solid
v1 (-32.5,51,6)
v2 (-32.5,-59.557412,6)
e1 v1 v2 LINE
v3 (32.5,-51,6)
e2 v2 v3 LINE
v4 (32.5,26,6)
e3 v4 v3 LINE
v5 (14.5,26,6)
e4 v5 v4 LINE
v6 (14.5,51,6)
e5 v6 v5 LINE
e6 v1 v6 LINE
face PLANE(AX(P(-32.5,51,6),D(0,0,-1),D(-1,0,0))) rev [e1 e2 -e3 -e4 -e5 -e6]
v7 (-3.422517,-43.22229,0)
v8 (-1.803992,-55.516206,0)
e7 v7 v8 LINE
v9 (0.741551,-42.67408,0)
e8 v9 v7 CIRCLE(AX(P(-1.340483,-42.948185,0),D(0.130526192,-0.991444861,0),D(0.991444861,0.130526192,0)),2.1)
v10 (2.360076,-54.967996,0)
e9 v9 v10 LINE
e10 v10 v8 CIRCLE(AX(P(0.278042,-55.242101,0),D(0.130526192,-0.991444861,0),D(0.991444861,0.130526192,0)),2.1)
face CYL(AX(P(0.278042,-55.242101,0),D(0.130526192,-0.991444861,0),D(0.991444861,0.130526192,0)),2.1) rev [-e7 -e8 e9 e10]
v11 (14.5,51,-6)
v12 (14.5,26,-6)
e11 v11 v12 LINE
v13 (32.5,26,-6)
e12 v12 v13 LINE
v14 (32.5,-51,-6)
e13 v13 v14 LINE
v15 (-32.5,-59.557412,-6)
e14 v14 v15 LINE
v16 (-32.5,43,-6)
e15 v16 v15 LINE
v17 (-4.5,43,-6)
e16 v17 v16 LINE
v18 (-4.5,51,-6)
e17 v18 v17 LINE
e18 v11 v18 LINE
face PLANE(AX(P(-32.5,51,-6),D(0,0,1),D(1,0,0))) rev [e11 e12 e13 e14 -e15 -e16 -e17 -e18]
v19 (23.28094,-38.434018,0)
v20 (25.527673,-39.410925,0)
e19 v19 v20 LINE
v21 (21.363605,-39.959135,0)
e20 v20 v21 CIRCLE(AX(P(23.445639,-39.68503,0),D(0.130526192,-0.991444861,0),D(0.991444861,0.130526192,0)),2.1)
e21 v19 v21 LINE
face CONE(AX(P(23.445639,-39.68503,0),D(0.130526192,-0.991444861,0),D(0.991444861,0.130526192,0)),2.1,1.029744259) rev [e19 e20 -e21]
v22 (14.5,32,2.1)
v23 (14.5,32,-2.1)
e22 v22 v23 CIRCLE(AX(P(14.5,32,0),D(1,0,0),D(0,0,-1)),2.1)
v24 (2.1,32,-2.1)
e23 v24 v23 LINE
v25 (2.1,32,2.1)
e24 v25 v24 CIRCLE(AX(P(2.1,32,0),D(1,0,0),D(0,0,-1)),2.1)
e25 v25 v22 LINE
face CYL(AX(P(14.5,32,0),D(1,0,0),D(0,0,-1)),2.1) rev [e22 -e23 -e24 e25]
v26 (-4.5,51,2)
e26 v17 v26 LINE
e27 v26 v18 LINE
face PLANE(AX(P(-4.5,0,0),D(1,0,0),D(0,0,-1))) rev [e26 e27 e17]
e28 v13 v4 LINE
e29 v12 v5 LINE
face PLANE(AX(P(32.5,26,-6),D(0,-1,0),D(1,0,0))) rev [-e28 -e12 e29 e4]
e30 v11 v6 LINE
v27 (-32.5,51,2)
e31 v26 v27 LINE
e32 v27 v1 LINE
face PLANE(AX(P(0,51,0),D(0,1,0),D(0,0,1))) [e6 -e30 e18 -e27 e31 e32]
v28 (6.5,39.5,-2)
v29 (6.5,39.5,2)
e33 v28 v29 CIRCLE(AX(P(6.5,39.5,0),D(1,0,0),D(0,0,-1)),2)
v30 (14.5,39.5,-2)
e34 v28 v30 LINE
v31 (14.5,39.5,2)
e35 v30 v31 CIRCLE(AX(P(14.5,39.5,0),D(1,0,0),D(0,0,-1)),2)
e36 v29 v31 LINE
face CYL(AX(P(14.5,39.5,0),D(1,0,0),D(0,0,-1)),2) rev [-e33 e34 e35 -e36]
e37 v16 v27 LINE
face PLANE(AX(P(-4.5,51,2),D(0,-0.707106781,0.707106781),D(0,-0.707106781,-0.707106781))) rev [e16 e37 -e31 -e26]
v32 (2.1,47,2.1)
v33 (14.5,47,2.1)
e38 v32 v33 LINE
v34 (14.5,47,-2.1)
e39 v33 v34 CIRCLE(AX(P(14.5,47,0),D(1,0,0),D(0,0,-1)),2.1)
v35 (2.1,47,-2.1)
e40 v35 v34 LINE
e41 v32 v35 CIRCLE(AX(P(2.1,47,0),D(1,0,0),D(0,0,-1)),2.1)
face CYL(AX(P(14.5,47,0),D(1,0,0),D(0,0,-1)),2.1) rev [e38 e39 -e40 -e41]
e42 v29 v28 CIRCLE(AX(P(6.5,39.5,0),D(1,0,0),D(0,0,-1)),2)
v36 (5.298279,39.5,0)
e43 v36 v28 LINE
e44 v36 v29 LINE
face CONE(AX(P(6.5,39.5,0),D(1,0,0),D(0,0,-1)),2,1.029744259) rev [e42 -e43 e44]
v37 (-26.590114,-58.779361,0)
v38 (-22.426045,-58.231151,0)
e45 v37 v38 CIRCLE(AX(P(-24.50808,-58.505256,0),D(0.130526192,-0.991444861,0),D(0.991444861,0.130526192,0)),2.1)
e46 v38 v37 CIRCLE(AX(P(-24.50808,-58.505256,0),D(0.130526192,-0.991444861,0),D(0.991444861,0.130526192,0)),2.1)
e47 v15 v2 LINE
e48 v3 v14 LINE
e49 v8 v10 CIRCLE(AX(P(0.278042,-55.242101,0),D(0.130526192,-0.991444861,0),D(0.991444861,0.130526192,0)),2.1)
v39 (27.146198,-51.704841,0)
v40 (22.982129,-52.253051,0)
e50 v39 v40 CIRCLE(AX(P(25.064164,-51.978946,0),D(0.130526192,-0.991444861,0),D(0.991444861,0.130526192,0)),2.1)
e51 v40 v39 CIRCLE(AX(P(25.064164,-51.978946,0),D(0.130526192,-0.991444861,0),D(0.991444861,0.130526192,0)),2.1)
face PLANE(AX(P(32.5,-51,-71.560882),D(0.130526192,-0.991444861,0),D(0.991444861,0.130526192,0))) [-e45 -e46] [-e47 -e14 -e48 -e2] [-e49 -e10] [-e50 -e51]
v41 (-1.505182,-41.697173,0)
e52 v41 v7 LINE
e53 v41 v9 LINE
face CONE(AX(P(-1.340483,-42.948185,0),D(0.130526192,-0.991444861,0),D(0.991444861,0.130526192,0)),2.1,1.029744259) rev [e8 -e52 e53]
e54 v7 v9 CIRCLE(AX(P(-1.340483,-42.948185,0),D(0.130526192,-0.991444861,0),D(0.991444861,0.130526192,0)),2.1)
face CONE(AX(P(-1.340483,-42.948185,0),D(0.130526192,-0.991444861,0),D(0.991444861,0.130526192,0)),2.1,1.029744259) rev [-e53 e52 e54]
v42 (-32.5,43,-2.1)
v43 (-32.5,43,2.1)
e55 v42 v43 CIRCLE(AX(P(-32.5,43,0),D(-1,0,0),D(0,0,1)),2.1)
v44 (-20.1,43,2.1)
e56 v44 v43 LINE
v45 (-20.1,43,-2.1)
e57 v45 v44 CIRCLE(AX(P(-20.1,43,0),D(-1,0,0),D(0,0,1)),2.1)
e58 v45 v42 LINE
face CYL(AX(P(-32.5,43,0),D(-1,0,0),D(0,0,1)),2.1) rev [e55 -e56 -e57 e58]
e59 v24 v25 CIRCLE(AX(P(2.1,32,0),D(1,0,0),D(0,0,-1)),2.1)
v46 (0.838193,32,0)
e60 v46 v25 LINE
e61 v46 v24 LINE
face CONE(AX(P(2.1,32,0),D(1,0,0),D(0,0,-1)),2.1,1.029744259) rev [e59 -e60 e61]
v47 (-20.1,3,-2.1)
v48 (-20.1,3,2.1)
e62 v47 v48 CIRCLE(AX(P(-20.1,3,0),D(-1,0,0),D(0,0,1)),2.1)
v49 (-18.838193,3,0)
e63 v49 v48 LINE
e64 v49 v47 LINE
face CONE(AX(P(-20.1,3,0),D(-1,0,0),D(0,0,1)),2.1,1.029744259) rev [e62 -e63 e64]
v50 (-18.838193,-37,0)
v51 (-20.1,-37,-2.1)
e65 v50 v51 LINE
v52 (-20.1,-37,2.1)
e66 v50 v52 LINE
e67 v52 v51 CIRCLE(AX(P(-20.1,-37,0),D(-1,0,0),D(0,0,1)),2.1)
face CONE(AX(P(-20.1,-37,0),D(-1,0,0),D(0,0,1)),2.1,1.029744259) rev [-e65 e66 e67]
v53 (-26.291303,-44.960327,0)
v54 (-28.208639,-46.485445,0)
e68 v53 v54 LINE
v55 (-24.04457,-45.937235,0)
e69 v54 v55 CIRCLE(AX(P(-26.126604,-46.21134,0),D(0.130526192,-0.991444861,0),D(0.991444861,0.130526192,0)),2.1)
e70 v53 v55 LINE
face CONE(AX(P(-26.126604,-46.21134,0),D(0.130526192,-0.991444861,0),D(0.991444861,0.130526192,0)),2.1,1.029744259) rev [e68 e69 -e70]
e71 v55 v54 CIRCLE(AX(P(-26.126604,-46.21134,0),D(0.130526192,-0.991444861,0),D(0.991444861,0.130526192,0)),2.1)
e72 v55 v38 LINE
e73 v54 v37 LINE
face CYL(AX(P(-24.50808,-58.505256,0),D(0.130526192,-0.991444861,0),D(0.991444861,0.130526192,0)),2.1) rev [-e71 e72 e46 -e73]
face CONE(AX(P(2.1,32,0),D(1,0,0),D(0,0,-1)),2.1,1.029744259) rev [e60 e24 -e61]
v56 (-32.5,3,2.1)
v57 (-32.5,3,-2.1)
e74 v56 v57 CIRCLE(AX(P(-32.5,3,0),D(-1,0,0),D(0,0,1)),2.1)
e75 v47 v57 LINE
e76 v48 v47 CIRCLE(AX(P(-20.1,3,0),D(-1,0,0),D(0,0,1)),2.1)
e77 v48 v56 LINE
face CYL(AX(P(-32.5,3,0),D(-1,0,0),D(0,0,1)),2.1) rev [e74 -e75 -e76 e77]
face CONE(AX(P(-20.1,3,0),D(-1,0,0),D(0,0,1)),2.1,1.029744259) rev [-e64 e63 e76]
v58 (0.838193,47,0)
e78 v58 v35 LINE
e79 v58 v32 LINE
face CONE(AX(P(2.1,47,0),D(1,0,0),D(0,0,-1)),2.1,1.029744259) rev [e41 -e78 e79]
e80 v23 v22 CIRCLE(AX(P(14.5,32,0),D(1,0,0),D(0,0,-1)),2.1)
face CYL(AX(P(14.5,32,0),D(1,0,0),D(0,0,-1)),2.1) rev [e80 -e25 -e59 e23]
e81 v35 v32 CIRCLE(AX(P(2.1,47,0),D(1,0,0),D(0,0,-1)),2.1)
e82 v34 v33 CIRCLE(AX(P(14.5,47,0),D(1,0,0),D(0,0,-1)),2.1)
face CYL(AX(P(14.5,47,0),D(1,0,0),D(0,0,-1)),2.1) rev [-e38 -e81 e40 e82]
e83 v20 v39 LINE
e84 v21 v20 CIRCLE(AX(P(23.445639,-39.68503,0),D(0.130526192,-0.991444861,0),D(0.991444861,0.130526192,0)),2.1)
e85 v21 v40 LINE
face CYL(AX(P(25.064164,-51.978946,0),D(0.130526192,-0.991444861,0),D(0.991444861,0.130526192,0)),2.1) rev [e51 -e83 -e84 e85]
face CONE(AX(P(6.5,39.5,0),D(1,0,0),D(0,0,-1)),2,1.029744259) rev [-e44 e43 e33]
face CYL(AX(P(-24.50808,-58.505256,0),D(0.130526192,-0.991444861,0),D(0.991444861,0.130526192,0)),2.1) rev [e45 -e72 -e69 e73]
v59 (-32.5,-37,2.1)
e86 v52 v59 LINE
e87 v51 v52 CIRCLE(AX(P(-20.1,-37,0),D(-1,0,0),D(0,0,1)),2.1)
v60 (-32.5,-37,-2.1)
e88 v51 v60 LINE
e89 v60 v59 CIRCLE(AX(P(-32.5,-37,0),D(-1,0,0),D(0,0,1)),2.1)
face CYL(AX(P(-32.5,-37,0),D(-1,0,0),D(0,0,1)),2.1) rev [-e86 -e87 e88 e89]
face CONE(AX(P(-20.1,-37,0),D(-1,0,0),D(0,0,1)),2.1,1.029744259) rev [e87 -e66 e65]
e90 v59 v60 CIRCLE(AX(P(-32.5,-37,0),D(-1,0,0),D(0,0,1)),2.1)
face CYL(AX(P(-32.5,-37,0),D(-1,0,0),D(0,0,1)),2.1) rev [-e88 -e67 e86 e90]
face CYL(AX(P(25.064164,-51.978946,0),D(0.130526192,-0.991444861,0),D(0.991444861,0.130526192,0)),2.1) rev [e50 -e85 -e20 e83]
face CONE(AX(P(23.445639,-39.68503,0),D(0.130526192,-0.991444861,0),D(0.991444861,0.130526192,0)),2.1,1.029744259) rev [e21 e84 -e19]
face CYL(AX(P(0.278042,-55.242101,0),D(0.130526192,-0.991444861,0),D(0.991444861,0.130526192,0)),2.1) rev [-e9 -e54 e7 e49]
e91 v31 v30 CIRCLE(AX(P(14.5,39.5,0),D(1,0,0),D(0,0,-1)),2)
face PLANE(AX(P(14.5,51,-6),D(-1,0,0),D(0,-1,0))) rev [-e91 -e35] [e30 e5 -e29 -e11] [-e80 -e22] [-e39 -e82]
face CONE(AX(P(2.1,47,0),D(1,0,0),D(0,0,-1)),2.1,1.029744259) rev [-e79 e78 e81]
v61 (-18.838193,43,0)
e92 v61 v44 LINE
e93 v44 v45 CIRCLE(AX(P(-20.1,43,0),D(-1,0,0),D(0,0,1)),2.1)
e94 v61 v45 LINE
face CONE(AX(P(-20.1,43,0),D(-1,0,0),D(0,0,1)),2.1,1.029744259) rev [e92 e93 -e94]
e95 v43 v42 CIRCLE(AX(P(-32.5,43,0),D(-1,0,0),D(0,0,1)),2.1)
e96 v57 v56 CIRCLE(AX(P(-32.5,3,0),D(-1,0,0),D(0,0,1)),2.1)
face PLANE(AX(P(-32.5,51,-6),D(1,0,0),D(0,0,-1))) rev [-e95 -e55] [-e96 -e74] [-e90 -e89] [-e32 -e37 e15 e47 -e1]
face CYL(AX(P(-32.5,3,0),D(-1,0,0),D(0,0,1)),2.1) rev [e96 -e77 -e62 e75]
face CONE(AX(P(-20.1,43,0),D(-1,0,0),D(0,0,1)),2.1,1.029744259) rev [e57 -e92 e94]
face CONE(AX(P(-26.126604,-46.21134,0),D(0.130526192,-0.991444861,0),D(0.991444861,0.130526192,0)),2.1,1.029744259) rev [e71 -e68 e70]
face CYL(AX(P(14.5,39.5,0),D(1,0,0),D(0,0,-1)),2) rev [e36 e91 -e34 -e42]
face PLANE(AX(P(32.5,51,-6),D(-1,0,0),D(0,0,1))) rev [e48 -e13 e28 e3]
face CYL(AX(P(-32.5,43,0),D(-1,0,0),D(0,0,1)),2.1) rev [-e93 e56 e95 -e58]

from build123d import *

# Parameters (mm, degrees)
SKETCH1_W                    = 65
SKETCH1_H                    = 12
BOSS_EXTRUDE1_DEPTH          = 51
BOSS_EXTRUDE2_DEPTH          = 12
SKETCH3_W                    = 18
SKETCH3_H                    = 25
CUT_EXTRUDE2_DEPTH           = 69.900909755
M5_TAPPED_HOLE1_D            = 4.2
M5_TAPPED_HOLE1_DEPTH        = 12.4
M5_TAPPED_HOLE1_TIP          = 1.2618073
M5_TAPPED_HOLE2_D            = 4.2
M5_TAPPED_HOLE2_DEPTH        = 12.4
M5_TAPPED_HOLE2_TIP          = 1.2618073
M5_TAPPED_HOLE3_D            = 4.2
M5_TAPPED_HOLE3_DEPTH        = 12.4
M5_TAPPED_HOLE3_TIP          = 1.2618073
CUT_EXTRUDE3_DEPTH           = 28
F_4_0_4_DIAMETER_HOLE1_D     = 4
F_4_0_4_DIAMETER_HOLE1_DEPTH = 8
F_4_0_4_DIAMETER_HOLE1_TIP   = 1.201721238


with BuildPart() as part:
    # Sketch1 → Boss-Extrude1 (new, symmetric)
    with BuildSketch(Plane(origin=(0, 0, 0), x_dir=(1, 0, 0), z_dir=(0, 1, 0))):
        Rectangle(SKETCH1_W, SKETCH1_H)
    extrude(amount=BOSS_EXTRUDE1_DEPTH, both=True)

    # Sketch4 → Boss-Extrude2 (add)
    with BuildSketch(Plane.XY.offset(6)):
        Polygon((-32.5, -51), (32.5, -51), (-32.5, -59.557412343), align=None)
    extrude(amount=-BOSS_EXTRUDE2_DEPTH)

    # Sketch3 → Cut-Extrude2 (cut, through all)
    with BuildSketch(Plane.XY.offset(6)):
        with Locations((23.5, 38.5)):
            Rectangle(SKETCH3_W, SKETCH3_H)
    extrude(amount=-CUT_EXTRUDE2_DEPTH, mode=Mode.SUBTRACT)

    # M5 Tapped Hole1
    with Locations(Plane(origin=(7.153590973, -54.336918053, 0), x_dir=(-0.9914448613738113, -0.13052619222004513, 0), z_dir=(0.13052619222004513, -0.9914448613738113, 0))):
        with Locations((-18.065122191, 0), (6.934877809, 0), (31.934877809, 0)):
            Hole(M5_TAPPED_HOLE1_D / 2, depth=M5_TAPPED_HOLE1_DEPTH)
            with Locations((0, 0, -(M5_TAPPED_HOLE1_DEPTH + M5_TAPPED_HOLE1_TIP / 2))):  # 118° drill point
                Cone(0, M5_TAPPED_HOLE1_D / 2, M5_TAPPED_HOLE1_TIP, mode=Mode.SUBTRACT)

    # M5 Tapped Hole2
    with Locations(Plane.ZY.offset(32.5)):
        with Locations((0, 43), (0, 3), (0, -37)):
            Hole(M5_TAPPED_HOLE2_D / 2, depth=M5_TAPPED_HOLE2_DEPTH)
            with Locations((0, 0, -(M5_TAPPED_HOLE2_DEPTH + M5_TAPPED_HOLE2_TIP / 2))):  # 118° drill point
                Cone(0, M5_TAPPED_HOLE2_D / 2, M5_TAPPED_HOLE2_TIP, mode=Mode.SUBTRACT)

    # M5 Tapped Hole3
    with Locations(Plane(origin=(14.5, 0, 0), x_dir=(0, 0, -1), z_dir=(1, 0, 0))):
        with Locations((0, 47), (0, 32)):
            Hole(M5_TAPPED_HOLE3_D / 2, depth=M5_TAPPED_HOLE3_DEPTH)
            with Locations((0, 0, -(M5_TAPPED_HOLE3_DEPTH + M5_TAPPED_HOLE3_TIP / 2))):  # 118° drill point
                Cone(0, M5_TAPPED_HOLE3_D / 2, M5_TAPPED_HOLE3_TIP, mode=Mode.SUBTRACT)

    # Sketch12 → Cut-Extrude3 (cut)
    with BuildSketch(Plane.ZY.offset(32.5)):
        Polygon((-6, 43), (-6, 51), (2, 51), align=None)
    extrude(amount=-CUT_EXTRUDE3_DEPTH, mode=Mode.SUBTRACT)

    # Ø4.0 (4) Diameter Hole1
    with Locations(Plane(origin=(14.5, 0, 0), x_dir=(0, 0, -1), z_dir=(1, 0, 0))):
        with Locations((0, 39.5)):
            Hole(F_4_0_4_DIAMETER_HOLE1_D / 2, depth=F_4_0_4_DIAMETER_HOLE1_DEPTH)
            with Locations((0, 0, -(F_4_0_4_DIAMETER_HOLE1_DEPTH + F_4_0_4_DIAMETER_HOLE1_TIP / 2))):  # 118° drill point
                Cone(0, F_4_0_4_DIAMETER_HOLE1_D / 2, F_4_0_4_DIAMETER_HOLE1_TIP, mode=Mode.SUBTRACT)


solid = part.part
